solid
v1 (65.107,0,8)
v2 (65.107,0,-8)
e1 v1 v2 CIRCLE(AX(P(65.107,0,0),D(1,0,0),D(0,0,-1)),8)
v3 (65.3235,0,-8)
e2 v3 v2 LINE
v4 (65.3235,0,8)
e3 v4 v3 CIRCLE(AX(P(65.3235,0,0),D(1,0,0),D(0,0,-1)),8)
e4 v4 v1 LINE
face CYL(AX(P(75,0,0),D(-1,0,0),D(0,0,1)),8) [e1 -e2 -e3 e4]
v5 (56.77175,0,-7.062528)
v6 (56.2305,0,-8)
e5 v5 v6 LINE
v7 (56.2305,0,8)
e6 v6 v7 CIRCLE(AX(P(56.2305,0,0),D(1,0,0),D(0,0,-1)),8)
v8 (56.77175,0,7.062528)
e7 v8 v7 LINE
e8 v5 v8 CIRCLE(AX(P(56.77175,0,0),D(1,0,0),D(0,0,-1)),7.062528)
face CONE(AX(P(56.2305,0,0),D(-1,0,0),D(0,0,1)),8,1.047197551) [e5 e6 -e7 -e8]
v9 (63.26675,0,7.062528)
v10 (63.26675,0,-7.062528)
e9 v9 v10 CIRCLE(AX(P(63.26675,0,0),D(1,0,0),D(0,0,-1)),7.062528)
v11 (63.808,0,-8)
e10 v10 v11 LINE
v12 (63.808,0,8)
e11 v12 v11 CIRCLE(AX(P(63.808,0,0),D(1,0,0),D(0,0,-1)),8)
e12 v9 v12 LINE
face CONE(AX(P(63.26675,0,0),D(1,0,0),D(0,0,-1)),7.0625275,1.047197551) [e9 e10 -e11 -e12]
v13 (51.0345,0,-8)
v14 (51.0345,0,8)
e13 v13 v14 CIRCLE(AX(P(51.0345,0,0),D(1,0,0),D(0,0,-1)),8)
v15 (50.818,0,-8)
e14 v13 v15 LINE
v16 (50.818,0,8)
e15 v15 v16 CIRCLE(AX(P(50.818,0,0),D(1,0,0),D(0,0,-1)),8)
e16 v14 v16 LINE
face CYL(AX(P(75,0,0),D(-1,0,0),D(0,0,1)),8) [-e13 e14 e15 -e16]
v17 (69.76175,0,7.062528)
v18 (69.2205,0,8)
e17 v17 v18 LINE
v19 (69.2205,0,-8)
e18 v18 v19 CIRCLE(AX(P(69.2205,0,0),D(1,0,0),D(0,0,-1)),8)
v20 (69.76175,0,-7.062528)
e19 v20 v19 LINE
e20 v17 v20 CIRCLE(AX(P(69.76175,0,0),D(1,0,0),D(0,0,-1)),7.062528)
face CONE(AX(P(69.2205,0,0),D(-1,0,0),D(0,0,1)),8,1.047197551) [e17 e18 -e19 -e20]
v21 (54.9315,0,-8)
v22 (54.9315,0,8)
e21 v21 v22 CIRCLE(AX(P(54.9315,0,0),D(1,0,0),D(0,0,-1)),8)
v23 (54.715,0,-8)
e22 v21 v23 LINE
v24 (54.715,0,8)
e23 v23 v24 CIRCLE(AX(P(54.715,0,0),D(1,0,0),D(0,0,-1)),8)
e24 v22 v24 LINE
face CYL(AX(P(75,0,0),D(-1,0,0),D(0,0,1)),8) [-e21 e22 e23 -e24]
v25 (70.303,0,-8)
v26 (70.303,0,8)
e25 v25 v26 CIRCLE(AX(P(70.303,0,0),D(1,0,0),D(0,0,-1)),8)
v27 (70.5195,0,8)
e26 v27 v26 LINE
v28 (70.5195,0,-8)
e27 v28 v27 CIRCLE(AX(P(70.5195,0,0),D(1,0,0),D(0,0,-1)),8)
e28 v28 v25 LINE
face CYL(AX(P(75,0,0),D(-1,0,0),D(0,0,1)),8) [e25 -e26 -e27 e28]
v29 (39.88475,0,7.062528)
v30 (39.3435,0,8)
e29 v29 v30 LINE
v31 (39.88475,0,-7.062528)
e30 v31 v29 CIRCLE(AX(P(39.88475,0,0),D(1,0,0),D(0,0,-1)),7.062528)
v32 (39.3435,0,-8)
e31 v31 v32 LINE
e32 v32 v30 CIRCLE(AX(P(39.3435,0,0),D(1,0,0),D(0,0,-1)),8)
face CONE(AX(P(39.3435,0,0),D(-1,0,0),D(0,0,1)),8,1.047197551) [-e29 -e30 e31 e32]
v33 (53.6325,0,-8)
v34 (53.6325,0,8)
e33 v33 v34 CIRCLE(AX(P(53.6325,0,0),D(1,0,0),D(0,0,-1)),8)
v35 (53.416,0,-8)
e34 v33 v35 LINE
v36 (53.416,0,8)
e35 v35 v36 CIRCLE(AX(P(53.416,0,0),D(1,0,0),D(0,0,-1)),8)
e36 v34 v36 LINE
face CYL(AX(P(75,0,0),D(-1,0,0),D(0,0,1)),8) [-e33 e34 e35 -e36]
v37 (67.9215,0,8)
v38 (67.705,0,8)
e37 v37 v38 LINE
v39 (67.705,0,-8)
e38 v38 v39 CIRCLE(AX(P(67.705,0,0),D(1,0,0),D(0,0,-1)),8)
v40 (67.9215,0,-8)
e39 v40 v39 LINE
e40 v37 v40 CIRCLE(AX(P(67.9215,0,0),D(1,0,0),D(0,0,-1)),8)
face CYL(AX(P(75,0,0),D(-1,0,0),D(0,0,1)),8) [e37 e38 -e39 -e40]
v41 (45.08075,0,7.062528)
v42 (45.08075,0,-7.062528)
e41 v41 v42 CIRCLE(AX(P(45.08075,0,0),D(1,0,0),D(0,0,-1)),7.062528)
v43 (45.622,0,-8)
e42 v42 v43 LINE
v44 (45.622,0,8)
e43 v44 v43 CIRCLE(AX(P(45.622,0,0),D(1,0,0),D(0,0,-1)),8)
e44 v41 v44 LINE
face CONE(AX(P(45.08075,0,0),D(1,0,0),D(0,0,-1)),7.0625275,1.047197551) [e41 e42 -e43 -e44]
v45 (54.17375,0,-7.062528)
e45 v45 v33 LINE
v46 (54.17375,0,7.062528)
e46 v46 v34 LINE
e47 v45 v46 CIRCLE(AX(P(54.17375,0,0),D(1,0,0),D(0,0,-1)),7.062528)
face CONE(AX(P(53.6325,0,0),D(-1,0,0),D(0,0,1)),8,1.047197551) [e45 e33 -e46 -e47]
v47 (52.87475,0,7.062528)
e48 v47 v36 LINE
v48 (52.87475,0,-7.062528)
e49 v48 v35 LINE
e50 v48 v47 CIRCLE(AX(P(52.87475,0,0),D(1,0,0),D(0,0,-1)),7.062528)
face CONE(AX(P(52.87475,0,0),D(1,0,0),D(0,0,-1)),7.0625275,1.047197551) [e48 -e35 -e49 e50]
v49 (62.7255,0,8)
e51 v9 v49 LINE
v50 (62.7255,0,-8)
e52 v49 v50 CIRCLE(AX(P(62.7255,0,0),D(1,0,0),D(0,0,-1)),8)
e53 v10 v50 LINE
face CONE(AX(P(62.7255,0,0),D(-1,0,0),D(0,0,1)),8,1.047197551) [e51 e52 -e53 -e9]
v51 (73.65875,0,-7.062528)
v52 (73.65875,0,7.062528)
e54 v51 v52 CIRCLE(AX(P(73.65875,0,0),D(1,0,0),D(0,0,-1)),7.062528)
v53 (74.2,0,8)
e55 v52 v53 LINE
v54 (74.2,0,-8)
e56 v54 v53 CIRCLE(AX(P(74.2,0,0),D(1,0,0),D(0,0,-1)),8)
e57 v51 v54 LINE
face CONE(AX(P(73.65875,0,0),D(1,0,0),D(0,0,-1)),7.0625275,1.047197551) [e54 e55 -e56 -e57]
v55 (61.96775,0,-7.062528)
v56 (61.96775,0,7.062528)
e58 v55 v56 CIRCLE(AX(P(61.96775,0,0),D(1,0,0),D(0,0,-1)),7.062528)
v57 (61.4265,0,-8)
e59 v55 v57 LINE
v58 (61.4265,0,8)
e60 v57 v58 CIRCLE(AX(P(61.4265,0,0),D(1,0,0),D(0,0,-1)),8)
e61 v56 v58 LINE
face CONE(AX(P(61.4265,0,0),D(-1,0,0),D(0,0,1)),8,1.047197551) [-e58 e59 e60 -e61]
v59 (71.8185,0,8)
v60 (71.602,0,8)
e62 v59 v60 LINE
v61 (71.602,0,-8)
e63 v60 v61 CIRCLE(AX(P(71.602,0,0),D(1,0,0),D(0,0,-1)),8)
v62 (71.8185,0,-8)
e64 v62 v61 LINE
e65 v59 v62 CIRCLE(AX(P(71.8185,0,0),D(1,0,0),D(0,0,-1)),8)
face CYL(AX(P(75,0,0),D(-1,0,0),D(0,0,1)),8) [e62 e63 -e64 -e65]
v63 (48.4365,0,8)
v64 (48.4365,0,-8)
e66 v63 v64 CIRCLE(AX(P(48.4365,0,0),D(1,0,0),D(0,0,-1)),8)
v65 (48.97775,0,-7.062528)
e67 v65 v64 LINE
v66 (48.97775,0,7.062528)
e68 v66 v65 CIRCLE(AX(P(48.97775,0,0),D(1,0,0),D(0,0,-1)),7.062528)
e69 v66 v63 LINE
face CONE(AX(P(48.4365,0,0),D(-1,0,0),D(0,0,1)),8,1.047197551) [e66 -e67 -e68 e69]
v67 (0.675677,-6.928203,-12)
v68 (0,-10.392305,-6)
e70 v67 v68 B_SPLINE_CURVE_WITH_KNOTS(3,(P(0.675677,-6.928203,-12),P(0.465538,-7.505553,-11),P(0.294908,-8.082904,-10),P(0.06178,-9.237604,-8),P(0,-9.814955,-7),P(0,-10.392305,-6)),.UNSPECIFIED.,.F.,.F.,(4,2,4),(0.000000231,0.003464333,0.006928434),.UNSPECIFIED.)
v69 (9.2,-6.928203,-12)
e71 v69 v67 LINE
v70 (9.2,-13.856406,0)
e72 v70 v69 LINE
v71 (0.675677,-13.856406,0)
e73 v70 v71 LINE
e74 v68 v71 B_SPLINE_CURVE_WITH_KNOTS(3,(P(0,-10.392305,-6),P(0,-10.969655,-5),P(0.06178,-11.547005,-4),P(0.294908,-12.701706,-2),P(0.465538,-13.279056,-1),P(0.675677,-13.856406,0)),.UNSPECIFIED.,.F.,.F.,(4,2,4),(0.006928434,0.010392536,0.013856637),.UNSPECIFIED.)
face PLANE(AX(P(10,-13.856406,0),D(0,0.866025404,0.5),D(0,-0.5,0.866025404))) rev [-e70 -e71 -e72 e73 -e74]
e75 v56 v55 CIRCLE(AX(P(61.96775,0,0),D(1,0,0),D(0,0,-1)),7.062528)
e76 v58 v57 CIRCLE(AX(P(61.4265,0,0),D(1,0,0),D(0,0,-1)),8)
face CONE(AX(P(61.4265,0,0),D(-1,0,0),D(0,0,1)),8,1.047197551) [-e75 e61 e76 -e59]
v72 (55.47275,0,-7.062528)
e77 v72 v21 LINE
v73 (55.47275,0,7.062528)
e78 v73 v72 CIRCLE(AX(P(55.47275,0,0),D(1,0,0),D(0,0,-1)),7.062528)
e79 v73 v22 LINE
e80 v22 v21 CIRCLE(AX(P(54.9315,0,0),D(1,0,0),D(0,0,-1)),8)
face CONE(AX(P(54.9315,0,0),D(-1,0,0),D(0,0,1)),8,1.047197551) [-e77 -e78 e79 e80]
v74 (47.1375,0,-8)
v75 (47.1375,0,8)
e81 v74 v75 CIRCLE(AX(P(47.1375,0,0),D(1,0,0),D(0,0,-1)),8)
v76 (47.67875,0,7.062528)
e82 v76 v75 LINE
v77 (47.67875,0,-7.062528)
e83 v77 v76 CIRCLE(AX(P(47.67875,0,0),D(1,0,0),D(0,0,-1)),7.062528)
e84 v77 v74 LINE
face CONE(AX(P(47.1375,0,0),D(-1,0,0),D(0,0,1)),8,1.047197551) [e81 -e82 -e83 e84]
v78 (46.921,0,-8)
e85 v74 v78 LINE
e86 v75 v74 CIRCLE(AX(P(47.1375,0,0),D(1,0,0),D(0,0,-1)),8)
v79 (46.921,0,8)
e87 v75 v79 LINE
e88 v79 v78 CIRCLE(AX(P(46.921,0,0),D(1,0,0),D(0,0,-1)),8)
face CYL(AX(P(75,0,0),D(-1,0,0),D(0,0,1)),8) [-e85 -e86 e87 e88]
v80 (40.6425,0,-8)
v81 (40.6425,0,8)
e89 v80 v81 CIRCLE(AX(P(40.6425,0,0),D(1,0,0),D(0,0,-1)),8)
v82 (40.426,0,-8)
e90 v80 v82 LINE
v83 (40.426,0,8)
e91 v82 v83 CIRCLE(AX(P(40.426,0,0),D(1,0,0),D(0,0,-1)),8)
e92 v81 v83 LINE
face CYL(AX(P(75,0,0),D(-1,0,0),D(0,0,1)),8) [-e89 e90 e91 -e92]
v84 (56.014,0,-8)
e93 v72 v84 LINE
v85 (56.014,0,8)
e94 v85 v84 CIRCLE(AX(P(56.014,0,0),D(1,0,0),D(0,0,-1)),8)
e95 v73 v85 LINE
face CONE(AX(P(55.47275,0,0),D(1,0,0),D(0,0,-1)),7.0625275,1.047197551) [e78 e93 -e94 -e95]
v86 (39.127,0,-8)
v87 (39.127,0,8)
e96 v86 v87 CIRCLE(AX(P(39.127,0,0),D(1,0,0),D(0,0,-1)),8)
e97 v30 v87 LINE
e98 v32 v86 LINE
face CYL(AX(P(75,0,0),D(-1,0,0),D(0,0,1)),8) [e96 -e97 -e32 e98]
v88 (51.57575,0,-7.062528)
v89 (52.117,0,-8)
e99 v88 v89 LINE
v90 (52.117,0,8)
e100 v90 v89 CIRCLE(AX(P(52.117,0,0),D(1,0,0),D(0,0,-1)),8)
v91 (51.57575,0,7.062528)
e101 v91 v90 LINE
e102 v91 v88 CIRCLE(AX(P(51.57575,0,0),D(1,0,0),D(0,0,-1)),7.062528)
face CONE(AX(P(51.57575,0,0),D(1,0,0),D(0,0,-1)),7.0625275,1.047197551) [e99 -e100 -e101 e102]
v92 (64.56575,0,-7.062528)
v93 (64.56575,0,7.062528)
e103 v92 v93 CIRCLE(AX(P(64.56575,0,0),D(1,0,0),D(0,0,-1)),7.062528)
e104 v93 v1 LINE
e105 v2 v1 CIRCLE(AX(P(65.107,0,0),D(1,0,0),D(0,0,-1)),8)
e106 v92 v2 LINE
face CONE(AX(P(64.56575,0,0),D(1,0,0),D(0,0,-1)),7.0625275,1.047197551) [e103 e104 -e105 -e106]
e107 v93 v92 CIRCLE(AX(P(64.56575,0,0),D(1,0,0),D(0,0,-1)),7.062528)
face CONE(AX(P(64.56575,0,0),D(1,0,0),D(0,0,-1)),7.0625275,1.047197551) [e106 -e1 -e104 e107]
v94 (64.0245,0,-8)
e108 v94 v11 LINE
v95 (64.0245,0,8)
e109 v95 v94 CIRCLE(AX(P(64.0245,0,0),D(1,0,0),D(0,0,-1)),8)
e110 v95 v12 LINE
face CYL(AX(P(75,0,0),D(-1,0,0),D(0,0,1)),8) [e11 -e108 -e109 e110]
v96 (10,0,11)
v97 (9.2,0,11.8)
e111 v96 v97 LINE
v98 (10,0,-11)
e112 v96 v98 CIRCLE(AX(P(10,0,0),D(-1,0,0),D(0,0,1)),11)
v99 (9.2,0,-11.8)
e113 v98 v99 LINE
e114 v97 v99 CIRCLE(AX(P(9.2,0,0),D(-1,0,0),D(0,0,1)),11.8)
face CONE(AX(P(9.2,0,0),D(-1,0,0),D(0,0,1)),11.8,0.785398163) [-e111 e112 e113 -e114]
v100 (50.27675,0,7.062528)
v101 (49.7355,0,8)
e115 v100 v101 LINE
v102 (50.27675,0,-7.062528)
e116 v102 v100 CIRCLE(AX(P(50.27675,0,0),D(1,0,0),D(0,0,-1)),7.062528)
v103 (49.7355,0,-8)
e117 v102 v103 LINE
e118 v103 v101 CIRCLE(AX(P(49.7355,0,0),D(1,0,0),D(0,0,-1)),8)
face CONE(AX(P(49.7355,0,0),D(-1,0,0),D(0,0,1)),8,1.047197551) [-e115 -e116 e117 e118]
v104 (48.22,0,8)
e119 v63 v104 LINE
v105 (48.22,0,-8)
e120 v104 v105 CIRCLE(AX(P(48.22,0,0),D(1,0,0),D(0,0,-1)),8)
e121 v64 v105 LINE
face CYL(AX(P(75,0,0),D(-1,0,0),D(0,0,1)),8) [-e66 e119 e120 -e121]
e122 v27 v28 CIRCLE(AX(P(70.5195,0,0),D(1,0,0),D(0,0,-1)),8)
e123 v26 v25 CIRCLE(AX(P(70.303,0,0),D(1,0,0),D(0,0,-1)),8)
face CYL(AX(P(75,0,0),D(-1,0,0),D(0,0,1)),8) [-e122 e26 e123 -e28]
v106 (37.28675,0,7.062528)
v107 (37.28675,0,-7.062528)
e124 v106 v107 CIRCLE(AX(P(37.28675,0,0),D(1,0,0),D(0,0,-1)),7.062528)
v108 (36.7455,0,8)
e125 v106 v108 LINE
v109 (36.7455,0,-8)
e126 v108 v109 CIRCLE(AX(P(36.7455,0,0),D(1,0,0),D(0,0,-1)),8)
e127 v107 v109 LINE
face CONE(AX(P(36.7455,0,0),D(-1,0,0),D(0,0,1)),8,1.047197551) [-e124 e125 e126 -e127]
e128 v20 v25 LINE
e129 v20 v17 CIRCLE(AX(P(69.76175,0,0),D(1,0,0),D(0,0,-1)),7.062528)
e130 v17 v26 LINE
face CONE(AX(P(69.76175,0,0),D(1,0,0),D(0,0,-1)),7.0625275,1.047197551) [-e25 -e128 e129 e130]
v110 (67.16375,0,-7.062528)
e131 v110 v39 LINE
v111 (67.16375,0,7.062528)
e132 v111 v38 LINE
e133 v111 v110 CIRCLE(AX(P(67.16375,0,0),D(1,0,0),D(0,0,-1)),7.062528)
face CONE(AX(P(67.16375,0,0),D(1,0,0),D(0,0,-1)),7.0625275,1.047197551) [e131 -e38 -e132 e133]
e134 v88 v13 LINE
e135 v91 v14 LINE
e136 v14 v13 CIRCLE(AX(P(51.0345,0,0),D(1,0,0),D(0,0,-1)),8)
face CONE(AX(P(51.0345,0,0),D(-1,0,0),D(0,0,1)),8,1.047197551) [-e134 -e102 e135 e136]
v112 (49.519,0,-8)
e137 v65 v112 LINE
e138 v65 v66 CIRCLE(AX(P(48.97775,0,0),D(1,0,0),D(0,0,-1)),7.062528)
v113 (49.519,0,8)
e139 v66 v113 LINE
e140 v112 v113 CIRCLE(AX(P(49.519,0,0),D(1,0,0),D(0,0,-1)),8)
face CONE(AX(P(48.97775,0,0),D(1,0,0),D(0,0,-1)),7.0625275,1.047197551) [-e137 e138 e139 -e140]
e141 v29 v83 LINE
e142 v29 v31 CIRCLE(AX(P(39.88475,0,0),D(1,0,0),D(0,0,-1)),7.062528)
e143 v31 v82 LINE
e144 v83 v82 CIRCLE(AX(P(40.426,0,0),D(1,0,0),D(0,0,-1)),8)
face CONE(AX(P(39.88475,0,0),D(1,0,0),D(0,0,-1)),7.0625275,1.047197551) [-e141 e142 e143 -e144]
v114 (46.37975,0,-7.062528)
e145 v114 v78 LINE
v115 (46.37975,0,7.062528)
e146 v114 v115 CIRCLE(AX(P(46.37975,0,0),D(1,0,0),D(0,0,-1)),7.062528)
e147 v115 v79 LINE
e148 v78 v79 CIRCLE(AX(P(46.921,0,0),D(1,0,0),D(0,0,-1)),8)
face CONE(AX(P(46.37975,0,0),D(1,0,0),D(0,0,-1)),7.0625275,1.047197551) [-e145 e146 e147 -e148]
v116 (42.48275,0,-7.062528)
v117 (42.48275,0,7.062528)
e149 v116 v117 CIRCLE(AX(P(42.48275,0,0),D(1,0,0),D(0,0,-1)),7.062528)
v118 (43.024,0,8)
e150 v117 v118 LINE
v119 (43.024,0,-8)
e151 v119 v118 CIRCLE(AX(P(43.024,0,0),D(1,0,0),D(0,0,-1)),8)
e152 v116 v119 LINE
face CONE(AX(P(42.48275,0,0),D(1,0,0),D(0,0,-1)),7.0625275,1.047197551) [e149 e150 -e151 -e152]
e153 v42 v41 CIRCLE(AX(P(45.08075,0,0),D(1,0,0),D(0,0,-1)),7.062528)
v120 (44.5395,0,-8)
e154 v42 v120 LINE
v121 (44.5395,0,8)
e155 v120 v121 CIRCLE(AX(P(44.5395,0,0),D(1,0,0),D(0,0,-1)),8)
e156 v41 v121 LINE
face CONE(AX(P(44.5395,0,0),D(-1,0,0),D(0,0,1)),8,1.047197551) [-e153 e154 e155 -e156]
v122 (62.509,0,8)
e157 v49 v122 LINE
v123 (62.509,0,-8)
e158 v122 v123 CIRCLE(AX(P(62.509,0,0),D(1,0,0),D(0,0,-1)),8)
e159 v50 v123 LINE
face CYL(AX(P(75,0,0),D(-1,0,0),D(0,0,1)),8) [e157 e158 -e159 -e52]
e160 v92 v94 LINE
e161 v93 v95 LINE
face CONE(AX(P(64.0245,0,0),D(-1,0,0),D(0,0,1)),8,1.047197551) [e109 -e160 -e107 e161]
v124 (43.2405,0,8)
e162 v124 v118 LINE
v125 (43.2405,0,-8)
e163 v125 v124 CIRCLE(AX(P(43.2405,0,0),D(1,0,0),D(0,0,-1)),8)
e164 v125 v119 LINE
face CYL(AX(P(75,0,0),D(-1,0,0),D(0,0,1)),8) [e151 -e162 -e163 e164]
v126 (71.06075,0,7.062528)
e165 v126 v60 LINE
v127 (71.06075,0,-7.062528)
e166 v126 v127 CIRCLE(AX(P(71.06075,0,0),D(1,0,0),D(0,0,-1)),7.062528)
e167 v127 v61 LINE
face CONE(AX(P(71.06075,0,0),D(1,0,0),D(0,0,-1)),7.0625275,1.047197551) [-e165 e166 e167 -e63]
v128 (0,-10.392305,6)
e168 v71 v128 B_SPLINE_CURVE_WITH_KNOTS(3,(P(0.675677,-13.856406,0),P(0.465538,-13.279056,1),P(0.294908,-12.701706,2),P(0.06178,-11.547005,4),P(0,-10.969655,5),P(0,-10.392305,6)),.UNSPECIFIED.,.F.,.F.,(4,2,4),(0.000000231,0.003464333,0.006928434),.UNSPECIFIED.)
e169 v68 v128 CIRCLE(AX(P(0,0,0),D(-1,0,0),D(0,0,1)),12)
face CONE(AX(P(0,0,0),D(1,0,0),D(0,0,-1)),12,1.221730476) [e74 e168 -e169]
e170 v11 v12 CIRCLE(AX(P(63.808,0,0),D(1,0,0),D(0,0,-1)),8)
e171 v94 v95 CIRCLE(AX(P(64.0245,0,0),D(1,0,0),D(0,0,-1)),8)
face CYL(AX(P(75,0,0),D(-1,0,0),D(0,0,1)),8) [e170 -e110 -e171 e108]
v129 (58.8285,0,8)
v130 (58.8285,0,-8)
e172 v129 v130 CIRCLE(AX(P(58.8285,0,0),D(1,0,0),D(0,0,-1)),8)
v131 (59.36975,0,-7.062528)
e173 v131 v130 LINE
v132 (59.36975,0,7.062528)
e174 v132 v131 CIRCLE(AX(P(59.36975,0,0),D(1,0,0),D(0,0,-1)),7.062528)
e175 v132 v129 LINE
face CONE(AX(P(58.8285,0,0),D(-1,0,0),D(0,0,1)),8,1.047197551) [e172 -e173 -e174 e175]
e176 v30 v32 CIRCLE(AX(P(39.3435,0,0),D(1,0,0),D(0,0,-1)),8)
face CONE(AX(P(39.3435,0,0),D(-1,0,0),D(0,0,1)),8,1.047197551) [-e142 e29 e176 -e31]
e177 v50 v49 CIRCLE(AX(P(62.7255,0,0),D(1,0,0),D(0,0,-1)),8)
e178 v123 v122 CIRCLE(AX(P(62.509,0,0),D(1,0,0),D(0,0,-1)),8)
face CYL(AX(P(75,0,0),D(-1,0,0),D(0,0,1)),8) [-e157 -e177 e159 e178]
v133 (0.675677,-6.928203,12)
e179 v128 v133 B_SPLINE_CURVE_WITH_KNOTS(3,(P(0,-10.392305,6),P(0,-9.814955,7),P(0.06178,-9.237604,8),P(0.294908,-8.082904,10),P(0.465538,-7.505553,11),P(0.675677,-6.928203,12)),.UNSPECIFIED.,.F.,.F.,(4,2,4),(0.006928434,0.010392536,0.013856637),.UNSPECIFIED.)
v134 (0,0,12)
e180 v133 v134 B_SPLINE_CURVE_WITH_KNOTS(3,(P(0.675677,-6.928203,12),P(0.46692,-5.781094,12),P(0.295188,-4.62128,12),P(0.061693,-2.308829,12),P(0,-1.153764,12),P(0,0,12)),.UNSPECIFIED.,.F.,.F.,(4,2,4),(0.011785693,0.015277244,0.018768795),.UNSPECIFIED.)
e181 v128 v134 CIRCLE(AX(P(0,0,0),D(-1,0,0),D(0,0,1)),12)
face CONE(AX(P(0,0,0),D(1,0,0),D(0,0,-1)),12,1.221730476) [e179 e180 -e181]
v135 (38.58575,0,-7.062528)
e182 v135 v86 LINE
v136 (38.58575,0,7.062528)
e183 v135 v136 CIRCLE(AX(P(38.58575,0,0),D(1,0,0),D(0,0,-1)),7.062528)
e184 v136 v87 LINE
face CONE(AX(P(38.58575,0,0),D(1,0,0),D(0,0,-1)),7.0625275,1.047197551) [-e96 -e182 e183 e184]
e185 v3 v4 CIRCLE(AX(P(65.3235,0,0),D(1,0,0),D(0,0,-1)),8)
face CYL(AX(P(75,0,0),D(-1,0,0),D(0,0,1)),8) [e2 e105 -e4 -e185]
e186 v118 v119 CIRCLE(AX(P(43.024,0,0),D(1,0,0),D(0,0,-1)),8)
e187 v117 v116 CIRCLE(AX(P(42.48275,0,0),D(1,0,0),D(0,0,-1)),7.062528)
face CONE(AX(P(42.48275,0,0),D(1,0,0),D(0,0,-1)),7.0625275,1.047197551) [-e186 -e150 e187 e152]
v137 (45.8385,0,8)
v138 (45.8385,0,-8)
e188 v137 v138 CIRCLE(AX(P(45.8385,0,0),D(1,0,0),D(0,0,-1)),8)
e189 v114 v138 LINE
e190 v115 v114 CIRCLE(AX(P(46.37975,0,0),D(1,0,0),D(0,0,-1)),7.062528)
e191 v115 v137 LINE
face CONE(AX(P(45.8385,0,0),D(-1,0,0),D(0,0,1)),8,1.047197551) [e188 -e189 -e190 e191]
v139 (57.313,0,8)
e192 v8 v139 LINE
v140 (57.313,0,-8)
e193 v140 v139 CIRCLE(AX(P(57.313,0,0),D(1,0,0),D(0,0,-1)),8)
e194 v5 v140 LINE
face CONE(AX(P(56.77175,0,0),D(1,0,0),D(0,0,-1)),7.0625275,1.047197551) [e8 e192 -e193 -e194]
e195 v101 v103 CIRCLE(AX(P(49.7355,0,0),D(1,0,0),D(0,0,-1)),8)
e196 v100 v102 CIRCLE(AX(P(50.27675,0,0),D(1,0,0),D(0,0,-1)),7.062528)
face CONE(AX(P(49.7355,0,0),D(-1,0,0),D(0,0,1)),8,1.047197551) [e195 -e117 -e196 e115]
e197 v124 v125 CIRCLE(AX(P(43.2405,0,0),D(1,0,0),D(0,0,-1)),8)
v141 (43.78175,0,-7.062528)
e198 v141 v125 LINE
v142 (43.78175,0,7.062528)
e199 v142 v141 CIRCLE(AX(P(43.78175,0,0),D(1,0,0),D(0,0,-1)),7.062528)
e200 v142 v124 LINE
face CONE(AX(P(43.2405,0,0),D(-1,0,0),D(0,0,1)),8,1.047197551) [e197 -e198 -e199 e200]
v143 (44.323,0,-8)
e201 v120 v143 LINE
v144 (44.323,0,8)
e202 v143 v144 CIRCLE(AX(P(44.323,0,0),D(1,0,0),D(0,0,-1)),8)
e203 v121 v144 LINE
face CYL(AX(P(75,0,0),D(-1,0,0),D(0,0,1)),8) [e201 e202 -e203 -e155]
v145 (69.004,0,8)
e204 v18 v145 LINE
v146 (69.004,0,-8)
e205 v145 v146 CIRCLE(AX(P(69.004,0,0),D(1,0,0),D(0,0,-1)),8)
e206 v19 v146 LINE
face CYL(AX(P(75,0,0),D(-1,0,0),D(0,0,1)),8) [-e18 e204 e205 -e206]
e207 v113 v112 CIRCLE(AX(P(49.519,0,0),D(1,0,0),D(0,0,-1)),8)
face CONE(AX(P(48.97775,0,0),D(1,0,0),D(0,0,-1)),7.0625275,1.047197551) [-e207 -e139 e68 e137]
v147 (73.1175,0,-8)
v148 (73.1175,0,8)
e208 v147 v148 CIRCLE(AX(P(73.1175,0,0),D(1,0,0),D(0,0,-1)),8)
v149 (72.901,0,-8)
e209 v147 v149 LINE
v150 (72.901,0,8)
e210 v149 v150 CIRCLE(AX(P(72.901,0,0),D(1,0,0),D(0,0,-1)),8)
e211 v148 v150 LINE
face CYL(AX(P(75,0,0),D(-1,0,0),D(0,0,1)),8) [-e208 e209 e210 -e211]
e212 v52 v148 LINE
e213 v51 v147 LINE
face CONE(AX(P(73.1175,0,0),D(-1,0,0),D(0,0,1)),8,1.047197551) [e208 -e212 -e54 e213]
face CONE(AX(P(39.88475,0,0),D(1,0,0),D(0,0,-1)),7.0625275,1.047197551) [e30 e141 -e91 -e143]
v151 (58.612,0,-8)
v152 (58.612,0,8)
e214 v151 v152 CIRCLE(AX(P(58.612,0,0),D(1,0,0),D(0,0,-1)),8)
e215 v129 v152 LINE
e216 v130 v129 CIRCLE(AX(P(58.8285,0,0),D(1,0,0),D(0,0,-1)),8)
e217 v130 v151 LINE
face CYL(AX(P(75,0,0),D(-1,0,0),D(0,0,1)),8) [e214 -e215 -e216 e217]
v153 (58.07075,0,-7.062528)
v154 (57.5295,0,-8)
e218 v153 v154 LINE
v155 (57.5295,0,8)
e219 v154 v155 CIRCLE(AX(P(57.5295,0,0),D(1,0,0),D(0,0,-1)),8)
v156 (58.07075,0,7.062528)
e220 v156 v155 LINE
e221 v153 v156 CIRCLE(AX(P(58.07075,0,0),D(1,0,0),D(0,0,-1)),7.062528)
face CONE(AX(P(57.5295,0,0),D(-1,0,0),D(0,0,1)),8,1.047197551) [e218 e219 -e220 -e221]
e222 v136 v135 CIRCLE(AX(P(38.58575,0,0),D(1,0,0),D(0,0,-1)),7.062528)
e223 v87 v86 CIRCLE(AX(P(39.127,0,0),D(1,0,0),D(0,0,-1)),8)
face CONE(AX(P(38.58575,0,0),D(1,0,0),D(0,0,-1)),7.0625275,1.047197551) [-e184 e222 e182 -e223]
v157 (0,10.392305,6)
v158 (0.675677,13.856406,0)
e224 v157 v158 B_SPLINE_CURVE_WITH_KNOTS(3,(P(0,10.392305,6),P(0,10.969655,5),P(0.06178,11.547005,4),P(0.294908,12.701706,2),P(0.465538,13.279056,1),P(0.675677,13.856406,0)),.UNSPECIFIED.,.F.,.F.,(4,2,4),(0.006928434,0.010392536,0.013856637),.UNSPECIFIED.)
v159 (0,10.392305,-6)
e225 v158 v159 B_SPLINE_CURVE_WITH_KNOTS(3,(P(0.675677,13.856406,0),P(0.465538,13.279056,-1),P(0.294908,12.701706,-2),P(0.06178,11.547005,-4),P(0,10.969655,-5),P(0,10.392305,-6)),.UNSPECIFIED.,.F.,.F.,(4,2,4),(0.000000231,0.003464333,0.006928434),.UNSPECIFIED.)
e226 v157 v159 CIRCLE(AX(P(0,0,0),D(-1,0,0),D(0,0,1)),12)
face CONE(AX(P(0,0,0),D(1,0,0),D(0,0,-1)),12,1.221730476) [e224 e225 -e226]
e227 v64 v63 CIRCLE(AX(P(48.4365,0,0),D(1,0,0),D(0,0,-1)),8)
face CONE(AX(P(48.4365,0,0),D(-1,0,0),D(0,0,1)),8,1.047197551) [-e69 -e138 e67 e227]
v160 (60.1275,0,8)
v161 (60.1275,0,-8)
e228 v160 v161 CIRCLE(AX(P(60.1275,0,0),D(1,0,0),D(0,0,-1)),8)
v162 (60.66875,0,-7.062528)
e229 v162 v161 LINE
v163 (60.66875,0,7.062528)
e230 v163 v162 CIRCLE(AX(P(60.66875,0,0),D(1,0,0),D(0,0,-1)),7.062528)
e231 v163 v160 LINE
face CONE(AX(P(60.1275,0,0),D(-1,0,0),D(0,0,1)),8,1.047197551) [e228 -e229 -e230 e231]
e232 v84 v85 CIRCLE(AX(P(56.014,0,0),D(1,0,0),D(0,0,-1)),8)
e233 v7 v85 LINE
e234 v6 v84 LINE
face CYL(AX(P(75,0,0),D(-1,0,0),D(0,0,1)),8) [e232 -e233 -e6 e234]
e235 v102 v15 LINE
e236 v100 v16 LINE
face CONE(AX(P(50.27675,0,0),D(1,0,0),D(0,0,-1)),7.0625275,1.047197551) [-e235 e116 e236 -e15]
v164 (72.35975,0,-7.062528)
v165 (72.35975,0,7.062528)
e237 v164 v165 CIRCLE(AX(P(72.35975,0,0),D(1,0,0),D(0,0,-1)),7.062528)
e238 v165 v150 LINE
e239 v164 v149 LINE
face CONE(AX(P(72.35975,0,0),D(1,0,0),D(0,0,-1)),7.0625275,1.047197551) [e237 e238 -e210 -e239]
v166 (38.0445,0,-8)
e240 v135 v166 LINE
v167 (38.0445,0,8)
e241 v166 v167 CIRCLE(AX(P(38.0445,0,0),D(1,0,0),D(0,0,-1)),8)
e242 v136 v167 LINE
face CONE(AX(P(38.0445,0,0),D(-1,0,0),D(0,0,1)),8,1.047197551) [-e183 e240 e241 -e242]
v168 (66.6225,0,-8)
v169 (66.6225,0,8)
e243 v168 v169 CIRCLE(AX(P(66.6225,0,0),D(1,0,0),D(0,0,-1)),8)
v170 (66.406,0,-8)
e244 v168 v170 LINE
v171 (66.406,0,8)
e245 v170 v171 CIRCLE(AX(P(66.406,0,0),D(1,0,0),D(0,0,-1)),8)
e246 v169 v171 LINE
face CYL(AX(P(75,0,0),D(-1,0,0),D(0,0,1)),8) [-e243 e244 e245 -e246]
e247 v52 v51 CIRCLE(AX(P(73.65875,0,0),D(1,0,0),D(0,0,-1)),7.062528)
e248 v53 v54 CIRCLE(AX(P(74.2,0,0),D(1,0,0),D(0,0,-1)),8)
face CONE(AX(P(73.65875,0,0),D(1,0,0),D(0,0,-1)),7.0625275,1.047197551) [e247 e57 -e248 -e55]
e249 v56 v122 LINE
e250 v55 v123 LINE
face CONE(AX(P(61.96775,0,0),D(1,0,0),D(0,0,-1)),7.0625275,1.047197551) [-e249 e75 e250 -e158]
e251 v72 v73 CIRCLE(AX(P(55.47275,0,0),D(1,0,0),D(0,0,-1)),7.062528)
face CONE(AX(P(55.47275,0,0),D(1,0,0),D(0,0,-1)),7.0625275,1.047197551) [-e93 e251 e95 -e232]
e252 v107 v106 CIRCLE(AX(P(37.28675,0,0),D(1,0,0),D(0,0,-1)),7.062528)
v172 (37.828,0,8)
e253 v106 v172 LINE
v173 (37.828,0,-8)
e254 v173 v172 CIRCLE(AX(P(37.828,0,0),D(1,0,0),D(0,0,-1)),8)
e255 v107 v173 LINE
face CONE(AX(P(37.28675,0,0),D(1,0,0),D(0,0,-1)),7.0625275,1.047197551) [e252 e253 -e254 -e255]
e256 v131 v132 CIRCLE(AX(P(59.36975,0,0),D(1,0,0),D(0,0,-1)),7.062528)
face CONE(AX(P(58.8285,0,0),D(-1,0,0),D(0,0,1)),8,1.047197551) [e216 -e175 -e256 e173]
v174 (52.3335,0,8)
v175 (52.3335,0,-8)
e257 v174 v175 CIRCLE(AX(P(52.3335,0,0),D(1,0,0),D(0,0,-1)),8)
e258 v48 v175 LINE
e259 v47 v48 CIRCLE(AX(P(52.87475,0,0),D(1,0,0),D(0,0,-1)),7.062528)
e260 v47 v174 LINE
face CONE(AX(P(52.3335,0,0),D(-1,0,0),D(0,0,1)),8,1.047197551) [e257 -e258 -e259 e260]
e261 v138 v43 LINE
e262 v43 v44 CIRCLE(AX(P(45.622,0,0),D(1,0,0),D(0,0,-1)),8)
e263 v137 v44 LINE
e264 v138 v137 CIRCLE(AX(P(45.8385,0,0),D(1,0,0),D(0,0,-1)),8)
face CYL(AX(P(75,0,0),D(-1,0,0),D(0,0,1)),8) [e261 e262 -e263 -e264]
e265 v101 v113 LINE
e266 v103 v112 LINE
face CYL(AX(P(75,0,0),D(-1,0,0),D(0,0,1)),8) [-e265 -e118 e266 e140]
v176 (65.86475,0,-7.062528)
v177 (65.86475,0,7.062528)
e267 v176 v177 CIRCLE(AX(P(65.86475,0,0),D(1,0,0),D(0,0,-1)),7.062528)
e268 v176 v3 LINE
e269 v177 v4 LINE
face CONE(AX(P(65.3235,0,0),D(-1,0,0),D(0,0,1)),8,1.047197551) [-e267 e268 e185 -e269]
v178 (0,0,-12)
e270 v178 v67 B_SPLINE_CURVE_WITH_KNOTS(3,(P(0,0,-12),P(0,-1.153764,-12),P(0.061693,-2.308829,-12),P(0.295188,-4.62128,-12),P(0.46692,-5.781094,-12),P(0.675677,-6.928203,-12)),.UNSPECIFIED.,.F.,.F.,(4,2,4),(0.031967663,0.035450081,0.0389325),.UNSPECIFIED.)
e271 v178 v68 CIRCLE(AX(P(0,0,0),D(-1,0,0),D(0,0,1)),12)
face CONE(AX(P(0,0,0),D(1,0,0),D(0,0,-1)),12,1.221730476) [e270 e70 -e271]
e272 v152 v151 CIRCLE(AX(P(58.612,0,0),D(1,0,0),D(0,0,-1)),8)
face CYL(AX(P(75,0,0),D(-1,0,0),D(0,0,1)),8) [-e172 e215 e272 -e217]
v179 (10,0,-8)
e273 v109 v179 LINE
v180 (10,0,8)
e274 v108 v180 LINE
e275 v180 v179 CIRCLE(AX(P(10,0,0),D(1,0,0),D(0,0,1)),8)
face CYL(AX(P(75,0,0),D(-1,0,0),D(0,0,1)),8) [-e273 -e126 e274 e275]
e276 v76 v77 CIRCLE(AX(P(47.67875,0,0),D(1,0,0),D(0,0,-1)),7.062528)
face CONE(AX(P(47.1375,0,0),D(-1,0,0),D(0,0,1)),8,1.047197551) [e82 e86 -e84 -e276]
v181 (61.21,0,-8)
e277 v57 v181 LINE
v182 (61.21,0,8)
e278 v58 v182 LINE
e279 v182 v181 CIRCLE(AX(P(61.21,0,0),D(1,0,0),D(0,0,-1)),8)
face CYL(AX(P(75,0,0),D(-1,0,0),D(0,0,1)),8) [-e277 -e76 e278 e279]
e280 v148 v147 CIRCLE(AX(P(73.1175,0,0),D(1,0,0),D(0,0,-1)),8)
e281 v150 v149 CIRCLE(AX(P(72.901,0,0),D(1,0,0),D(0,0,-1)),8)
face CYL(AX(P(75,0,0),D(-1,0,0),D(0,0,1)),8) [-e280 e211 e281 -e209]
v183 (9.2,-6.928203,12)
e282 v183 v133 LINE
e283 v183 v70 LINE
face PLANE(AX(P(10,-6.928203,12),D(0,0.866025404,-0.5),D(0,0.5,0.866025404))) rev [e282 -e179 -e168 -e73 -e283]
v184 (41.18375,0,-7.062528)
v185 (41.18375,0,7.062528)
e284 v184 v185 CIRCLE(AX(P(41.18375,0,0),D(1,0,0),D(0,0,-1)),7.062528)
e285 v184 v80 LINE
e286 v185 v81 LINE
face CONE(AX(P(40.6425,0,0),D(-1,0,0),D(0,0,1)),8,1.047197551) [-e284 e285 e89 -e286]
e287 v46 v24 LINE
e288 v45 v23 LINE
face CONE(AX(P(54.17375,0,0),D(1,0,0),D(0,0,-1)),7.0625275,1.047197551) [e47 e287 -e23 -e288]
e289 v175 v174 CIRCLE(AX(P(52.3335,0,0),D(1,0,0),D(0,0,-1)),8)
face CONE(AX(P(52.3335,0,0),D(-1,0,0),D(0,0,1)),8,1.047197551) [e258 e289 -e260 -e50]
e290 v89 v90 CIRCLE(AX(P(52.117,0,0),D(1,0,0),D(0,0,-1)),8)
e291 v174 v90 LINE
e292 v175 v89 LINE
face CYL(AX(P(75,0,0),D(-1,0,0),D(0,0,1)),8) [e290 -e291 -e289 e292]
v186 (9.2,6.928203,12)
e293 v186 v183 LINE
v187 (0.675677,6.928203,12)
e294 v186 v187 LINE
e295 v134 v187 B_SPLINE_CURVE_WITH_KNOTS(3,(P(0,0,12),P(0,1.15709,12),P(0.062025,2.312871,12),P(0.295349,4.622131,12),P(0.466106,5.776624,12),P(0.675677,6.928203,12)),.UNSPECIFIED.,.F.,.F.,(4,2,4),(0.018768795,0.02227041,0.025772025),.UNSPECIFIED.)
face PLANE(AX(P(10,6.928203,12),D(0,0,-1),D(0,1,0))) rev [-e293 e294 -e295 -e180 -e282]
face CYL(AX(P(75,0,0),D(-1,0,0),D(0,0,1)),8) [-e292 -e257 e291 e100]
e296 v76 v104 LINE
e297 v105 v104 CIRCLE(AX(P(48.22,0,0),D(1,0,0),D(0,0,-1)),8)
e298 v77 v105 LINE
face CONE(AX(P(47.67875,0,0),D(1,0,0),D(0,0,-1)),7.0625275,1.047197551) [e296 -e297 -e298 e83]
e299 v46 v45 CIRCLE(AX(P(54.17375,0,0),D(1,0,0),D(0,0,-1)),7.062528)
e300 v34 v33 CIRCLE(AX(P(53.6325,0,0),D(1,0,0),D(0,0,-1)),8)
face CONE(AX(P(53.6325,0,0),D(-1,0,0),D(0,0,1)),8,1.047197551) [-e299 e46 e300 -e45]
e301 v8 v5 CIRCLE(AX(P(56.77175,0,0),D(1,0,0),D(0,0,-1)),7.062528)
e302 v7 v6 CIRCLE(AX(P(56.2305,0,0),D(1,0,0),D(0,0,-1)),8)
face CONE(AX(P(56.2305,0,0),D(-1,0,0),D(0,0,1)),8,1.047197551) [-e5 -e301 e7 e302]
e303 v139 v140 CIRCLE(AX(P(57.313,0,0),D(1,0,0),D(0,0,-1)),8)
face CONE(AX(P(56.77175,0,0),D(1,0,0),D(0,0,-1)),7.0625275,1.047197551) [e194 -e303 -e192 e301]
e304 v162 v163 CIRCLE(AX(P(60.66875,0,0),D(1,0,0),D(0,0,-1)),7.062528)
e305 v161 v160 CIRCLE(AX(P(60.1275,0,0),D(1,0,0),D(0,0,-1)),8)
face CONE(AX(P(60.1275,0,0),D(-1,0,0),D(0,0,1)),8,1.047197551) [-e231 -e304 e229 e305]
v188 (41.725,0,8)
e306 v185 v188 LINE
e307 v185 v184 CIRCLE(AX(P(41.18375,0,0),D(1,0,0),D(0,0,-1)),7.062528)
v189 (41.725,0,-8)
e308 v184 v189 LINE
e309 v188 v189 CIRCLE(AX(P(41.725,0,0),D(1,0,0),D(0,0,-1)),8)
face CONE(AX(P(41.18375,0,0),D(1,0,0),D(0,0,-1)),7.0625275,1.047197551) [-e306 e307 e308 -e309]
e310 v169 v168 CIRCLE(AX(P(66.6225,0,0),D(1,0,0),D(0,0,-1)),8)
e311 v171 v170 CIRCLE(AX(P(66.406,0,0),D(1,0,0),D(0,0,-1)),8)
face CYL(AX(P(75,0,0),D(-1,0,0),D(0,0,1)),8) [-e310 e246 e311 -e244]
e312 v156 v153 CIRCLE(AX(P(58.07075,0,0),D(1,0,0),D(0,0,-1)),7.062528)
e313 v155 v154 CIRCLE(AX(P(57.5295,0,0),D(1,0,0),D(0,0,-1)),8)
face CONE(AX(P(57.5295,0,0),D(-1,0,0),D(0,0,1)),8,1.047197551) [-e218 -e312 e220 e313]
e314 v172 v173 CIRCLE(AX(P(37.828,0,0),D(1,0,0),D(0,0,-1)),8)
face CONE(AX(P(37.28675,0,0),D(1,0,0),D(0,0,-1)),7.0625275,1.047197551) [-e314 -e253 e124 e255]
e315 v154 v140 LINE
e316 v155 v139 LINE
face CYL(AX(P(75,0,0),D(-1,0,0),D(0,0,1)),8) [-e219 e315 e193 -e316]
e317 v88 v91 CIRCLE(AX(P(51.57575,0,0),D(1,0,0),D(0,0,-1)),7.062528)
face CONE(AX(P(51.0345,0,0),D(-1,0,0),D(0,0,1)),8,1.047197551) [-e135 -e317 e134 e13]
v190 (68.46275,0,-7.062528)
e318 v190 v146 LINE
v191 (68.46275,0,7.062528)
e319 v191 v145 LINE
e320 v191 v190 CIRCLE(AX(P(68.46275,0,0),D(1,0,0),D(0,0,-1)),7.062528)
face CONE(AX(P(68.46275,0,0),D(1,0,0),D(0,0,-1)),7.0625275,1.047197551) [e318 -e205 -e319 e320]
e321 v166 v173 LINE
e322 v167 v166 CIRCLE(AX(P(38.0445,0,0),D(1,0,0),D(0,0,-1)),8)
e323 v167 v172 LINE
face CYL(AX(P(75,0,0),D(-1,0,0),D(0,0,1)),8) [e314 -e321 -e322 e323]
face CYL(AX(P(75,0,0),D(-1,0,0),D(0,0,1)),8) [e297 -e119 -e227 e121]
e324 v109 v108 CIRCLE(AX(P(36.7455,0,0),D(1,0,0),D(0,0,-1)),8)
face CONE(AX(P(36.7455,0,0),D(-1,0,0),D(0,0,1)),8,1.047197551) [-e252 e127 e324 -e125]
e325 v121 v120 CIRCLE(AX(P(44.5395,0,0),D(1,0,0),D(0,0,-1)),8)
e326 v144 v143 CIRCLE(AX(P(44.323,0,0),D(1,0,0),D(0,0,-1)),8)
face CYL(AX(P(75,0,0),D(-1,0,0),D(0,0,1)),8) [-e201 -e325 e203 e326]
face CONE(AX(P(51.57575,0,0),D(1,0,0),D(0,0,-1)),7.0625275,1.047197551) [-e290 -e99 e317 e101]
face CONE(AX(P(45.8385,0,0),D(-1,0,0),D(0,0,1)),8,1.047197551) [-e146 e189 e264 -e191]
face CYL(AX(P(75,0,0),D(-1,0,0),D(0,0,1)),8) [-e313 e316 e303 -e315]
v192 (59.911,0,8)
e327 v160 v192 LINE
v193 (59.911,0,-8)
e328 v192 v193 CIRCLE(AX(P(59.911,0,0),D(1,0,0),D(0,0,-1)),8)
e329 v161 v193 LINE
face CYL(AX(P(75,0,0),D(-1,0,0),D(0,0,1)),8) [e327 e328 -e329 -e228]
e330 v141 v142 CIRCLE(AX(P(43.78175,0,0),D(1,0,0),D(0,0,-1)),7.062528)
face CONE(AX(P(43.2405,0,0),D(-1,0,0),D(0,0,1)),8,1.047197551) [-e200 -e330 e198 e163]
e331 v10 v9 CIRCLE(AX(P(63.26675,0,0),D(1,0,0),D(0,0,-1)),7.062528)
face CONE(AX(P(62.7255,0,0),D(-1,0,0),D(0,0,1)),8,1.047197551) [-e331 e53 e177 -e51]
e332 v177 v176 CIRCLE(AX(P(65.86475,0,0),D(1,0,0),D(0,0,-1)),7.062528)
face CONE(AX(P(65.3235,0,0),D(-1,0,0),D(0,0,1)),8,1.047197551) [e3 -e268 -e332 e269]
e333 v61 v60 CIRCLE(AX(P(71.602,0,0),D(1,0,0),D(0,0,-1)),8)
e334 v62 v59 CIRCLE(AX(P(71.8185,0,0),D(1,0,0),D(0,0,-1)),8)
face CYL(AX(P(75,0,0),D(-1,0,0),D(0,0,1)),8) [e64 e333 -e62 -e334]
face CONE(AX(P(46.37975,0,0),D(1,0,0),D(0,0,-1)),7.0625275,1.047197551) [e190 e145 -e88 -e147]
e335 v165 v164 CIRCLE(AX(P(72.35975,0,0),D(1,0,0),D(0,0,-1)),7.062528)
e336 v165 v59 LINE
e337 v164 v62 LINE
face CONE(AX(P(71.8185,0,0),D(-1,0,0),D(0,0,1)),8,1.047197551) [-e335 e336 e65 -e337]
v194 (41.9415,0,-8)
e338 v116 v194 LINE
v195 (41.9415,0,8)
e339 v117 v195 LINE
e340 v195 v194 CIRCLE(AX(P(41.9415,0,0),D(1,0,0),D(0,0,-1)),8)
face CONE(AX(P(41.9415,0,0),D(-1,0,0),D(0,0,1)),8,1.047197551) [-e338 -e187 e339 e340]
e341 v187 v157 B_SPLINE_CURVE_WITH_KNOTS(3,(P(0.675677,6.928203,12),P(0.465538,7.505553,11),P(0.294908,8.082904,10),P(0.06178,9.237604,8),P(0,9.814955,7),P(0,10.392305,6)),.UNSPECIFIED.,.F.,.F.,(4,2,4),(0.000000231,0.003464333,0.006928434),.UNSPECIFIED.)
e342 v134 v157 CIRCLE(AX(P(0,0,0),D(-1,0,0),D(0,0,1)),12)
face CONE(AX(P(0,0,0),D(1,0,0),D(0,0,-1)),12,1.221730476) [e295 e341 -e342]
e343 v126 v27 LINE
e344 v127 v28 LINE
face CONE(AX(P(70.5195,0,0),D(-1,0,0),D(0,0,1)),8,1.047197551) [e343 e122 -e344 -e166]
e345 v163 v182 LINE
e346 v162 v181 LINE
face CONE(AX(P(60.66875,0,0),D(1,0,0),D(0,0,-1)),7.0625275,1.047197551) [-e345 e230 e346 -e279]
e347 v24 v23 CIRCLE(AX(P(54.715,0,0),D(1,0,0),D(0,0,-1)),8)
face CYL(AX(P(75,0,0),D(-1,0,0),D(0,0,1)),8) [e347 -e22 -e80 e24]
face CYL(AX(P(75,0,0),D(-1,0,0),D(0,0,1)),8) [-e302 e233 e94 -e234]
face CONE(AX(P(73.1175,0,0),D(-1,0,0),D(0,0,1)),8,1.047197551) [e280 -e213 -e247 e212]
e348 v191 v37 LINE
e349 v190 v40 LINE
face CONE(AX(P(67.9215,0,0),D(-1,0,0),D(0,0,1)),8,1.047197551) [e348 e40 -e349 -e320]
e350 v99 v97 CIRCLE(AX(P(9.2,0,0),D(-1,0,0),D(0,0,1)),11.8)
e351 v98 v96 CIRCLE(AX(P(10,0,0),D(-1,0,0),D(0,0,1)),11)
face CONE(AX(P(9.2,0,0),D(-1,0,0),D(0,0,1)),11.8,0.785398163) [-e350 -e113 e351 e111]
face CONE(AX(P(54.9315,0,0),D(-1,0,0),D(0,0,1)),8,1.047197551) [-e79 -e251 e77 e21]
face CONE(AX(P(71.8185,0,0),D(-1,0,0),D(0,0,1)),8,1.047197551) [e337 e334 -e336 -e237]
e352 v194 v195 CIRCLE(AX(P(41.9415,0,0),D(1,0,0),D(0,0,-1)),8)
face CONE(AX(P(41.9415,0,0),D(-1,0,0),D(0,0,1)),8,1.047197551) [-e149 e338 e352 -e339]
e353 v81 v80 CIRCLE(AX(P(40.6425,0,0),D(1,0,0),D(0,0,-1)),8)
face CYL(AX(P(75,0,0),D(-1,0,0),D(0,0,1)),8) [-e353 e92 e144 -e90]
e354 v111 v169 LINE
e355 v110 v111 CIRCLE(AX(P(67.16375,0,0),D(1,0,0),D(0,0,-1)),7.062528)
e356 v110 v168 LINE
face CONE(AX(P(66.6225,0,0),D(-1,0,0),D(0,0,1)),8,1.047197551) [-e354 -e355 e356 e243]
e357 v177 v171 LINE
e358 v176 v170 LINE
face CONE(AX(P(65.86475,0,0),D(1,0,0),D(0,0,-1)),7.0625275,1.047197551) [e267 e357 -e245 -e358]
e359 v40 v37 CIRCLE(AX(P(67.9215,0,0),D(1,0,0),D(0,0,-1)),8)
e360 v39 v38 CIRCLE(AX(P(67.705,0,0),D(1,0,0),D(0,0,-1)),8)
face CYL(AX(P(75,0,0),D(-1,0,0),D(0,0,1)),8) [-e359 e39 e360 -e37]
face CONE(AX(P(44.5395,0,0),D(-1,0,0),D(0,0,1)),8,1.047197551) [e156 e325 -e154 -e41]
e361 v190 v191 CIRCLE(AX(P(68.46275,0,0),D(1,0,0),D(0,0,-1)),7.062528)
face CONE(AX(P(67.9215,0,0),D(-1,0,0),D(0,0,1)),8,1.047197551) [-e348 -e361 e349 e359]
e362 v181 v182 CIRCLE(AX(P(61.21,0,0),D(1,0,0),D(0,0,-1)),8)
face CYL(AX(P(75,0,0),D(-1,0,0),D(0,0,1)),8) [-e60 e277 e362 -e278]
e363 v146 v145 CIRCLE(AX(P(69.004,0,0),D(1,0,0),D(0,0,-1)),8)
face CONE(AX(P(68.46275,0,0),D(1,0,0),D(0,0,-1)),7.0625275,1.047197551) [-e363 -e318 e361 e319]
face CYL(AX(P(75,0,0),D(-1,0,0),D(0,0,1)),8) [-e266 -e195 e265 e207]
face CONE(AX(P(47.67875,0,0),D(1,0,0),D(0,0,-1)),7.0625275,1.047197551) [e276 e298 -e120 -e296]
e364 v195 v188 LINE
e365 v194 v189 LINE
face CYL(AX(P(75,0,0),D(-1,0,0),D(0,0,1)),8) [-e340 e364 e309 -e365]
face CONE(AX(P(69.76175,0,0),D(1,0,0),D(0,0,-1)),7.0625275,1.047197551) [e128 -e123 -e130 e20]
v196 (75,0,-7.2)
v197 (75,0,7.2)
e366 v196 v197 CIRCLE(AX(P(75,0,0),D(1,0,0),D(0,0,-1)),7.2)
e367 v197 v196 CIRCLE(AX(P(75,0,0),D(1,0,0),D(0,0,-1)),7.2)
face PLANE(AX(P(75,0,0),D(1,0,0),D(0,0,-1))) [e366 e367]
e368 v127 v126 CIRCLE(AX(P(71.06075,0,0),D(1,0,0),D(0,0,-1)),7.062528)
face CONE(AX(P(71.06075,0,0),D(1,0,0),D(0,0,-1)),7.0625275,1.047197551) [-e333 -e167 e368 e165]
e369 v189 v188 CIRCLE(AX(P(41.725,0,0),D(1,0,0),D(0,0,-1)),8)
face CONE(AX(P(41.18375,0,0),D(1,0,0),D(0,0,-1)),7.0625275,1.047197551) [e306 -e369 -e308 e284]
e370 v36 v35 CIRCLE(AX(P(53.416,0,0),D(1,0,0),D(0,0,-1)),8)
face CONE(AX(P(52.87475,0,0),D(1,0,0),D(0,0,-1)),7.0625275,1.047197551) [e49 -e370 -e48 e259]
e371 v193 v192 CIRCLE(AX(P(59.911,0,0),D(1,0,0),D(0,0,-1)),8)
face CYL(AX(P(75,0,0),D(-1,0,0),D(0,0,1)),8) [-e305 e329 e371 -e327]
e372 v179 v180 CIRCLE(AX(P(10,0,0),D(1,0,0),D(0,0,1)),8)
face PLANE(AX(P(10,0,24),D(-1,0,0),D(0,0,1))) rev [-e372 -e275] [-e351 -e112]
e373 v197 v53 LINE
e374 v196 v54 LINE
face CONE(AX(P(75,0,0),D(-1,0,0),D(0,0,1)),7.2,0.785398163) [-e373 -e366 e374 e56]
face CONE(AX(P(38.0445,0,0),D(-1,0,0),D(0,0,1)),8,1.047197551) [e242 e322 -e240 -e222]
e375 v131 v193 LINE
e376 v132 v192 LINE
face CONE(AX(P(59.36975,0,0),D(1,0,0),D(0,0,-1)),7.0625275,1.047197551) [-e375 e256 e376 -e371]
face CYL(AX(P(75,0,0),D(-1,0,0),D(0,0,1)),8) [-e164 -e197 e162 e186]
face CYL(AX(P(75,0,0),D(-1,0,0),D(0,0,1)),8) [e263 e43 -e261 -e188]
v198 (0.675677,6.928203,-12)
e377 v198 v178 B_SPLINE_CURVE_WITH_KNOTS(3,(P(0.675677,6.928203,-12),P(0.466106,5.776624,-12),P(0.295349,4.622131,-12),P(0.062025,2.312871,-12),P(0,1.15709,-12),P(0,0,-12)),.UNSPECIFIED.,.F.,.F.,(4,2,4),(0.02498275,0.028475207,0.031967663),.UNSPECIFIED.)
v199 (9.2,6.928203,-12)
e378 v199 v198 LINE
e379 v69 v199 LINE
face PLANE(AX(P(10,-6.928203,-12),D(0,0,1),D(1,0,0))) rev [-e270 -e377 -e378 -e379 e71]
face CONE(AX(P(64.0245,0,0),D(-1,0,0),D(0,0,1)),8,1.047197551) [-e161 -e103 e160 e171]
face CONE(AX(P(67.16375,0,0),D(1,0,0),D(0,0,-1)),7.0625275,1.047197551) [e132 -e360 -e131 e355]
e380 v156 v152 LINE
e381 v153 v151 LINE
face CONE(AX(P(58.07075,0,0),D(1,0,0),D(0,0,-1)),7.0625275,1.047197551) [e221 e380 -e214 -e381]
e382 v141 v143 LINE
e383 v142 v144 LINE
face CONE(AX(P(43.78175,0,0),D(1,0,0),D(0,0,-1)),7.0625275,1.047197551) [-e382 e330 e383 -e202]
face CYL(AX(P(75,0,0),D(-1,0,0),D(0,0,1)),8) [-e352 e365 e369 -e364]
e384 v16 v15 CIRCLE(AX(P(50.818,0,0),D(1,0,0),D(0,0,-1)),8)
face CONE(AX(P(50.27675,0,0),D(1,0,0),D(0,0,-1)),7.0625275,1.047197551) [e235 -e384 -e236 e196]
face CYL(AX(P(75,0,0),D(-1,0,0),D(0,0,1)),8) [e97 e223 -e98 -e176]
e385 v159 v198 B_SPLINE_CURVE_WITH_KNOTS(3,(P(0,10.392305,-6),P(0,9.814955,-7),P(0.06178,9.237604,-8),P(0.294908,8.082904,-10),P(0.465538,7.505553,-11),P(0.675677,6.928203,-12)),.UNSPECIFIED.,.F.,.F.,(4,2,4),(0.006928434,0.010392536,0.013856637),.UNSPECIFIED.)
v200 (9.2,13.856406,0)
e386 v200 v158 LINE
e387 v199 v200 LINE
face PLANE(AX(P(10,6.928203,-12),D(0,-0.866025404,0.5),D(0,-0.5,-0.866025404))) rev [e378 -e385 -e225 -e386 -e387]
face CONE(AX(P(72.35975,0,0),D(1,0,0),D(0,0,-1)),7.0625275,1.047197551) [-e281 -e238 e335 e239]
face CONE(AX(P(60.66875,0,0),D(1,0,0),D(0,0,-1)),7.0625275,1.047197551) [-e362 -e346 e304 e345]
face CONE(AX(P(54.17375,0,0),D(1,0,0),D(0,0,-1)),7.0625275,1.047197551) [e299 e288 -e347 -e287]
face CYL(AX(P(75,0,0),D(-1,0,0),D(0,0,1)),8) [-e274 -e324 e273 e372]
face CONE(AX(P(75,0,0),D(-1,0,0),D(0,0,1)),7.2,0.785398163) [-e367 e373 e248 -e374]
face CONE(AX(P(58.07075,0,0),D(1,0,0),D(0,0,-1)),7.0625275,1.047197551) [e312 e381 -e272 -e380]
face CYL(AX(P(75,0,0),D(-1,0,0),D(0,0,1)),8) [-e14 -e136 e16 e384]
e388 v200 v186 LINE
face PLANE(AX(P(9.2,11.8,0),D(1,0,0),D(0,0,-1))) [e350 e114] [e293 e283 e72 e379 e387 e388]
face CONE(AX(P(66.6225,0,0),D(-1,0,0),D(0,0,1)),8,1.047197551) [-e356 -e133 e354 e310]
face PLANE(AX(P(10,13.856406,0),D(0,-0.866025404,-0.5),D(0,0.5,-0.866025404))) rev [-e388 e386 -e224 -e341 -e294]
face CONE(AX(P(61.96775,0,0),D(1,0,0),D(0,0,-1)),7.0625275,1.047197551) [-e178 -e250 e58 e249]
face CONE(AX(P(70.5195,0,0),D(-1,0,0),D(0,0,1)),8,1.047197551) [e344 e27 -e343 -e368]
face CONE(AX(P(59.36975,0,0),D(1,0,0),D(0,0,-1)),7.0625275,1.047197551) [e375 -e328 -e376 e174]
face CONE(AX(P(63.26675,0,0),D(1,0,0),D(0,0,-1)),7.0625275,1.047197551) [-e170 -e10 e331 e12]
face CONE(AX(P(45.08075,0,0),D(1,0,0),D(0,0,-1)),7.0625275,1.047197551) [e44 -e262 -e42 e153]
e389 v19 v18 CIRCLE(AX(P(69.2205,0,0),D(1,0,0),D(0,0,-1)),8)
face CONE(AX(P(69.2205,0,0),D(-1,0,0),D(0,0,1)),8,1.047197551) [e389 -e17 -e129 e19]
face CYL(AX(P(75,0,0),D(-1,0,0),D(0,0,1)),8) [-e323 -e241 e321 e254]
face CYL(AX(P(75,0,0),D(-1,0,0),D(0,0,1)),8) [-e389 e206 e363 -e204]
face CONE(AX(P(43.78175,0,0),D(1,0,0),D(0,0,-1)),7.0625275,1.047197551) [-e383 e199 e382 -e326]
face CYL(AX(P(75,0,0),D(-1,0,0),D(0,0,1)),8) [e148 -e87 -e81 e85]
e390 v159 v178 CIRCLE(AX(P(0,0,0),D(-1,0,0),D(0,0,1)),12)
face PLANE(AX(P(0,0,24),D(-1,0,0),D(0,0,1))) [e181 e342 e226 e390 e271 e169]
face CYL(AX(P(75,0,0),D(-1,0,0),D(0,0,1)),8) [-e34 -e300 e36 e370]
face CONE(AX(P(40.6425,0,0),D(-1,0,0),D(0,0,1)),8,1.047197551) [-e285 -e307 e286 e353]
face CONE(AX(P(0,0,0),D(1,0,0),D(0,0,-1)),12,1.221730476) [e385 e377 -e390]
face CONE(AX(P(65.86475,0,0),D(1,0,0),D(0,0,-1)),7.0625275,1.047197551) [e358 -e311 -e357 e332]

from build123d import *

# Parameters (mm, degrees)
BASEHEAD_DEPTH   = 10
SKETCH5_R        = 8
BASEBODY_DEPTH   = 65
CHAMFER1_SIZE    = 0.8
LPATTERN10_COUNT = 29
LPATTERN10_PITCH = 1.299


with BuildPart() as part:
    # Sketch2 → BaseHead (new body)
    with BuildSketch(Plane(origin=(0, 0, 0), x_dir=(0, 0, -1), z_dir=(1, 0, 0))):
        Polygon((0, -13.856406461), (12, -6.92820323), (12, 6.92820323), (0, 13.856406461), (-12, 6.92820323), (-12, -6.92820323), align=None)
    extrude(amount=BASEHEAD_DEPTH)

    # Sketch3 → BearingFace (revolve, cut)
    with BuildSketch(Plane.XY, mode=Mode.PRIVATE) as bearingface_sk:
        Polygon((10, 13.856406461), (10, 11), (9.2, 11.8), (9.2, 13.856406461), align=None)
    revolve(bearingface_sk.sketch.rotate(Axis((-0.957090588, 0, 0), (1, 0, 0)), 90), axis=Axis((-0.957090588, 0, 0), (1, 0, 0)), mode=Mode.SUBTRACT)

    # Sketch4 → HeadChamfer (revolve, cut)
    with BuildSketch(Plane.XY):
        Polygon((0, 13.856406461), (0.675676694, 13.856406461), (0, 12), align=None)
    revolve(axis=Axis((-0.493528746, 0, 0), (1, 0, 0)), mode=Mode.SUBTRACT)

    # Sketch5 → BaseBody (add)
    with BuildSketch(Plane(origin=(10, 0, 0), x_dir=(0, 0, -1), z_dir=(1, 0, 0))):
        with Locations(Location((0, 0, 0), (0, 0, 180))):
            Circle(SKETCH5_R)
    extrude(amount=BASEBODY_DEPTH)

    # Chamfer1
    chamfer1_edges = [part.edges().sort_by_distance(p)[0] for p in [
        (75, 0, -8),
    ]]
    chamfer(chamfer1_edges, length=CHAMFER1_SIZE)

    # Sketch6 → Cut-Revolve10 (revolve, cut)
    with BuildSketch(Plane.XY, mode=Mode.PRIVATE) as cut_revolve10_sk:
        Polygon((73.1175, 9.0825), (74.2, 9.0825), (74.2, 8), (73.65875, 7.0625275), (73.1175, 8), align=None)
    cut_revolve10 = revolve(cut_revolve10_sk.sketch.rotate(Axis((75, 0, 0), (-1, 0, 0)), 90), axis=Axis((75, 0, 0), (-1, 0, 0)), mode=Mode.SUBTRACT)

    # LPattern10: Cut-Revolve10 ×29
    with Locations(*[(-i * LPATTERN10_PITCH, 0, 0) for i in range(1, LPATTERN10_COUNT)]):
        add(cut_revolve10, mode=Mode.SUBTRACT)


solid = part.part
